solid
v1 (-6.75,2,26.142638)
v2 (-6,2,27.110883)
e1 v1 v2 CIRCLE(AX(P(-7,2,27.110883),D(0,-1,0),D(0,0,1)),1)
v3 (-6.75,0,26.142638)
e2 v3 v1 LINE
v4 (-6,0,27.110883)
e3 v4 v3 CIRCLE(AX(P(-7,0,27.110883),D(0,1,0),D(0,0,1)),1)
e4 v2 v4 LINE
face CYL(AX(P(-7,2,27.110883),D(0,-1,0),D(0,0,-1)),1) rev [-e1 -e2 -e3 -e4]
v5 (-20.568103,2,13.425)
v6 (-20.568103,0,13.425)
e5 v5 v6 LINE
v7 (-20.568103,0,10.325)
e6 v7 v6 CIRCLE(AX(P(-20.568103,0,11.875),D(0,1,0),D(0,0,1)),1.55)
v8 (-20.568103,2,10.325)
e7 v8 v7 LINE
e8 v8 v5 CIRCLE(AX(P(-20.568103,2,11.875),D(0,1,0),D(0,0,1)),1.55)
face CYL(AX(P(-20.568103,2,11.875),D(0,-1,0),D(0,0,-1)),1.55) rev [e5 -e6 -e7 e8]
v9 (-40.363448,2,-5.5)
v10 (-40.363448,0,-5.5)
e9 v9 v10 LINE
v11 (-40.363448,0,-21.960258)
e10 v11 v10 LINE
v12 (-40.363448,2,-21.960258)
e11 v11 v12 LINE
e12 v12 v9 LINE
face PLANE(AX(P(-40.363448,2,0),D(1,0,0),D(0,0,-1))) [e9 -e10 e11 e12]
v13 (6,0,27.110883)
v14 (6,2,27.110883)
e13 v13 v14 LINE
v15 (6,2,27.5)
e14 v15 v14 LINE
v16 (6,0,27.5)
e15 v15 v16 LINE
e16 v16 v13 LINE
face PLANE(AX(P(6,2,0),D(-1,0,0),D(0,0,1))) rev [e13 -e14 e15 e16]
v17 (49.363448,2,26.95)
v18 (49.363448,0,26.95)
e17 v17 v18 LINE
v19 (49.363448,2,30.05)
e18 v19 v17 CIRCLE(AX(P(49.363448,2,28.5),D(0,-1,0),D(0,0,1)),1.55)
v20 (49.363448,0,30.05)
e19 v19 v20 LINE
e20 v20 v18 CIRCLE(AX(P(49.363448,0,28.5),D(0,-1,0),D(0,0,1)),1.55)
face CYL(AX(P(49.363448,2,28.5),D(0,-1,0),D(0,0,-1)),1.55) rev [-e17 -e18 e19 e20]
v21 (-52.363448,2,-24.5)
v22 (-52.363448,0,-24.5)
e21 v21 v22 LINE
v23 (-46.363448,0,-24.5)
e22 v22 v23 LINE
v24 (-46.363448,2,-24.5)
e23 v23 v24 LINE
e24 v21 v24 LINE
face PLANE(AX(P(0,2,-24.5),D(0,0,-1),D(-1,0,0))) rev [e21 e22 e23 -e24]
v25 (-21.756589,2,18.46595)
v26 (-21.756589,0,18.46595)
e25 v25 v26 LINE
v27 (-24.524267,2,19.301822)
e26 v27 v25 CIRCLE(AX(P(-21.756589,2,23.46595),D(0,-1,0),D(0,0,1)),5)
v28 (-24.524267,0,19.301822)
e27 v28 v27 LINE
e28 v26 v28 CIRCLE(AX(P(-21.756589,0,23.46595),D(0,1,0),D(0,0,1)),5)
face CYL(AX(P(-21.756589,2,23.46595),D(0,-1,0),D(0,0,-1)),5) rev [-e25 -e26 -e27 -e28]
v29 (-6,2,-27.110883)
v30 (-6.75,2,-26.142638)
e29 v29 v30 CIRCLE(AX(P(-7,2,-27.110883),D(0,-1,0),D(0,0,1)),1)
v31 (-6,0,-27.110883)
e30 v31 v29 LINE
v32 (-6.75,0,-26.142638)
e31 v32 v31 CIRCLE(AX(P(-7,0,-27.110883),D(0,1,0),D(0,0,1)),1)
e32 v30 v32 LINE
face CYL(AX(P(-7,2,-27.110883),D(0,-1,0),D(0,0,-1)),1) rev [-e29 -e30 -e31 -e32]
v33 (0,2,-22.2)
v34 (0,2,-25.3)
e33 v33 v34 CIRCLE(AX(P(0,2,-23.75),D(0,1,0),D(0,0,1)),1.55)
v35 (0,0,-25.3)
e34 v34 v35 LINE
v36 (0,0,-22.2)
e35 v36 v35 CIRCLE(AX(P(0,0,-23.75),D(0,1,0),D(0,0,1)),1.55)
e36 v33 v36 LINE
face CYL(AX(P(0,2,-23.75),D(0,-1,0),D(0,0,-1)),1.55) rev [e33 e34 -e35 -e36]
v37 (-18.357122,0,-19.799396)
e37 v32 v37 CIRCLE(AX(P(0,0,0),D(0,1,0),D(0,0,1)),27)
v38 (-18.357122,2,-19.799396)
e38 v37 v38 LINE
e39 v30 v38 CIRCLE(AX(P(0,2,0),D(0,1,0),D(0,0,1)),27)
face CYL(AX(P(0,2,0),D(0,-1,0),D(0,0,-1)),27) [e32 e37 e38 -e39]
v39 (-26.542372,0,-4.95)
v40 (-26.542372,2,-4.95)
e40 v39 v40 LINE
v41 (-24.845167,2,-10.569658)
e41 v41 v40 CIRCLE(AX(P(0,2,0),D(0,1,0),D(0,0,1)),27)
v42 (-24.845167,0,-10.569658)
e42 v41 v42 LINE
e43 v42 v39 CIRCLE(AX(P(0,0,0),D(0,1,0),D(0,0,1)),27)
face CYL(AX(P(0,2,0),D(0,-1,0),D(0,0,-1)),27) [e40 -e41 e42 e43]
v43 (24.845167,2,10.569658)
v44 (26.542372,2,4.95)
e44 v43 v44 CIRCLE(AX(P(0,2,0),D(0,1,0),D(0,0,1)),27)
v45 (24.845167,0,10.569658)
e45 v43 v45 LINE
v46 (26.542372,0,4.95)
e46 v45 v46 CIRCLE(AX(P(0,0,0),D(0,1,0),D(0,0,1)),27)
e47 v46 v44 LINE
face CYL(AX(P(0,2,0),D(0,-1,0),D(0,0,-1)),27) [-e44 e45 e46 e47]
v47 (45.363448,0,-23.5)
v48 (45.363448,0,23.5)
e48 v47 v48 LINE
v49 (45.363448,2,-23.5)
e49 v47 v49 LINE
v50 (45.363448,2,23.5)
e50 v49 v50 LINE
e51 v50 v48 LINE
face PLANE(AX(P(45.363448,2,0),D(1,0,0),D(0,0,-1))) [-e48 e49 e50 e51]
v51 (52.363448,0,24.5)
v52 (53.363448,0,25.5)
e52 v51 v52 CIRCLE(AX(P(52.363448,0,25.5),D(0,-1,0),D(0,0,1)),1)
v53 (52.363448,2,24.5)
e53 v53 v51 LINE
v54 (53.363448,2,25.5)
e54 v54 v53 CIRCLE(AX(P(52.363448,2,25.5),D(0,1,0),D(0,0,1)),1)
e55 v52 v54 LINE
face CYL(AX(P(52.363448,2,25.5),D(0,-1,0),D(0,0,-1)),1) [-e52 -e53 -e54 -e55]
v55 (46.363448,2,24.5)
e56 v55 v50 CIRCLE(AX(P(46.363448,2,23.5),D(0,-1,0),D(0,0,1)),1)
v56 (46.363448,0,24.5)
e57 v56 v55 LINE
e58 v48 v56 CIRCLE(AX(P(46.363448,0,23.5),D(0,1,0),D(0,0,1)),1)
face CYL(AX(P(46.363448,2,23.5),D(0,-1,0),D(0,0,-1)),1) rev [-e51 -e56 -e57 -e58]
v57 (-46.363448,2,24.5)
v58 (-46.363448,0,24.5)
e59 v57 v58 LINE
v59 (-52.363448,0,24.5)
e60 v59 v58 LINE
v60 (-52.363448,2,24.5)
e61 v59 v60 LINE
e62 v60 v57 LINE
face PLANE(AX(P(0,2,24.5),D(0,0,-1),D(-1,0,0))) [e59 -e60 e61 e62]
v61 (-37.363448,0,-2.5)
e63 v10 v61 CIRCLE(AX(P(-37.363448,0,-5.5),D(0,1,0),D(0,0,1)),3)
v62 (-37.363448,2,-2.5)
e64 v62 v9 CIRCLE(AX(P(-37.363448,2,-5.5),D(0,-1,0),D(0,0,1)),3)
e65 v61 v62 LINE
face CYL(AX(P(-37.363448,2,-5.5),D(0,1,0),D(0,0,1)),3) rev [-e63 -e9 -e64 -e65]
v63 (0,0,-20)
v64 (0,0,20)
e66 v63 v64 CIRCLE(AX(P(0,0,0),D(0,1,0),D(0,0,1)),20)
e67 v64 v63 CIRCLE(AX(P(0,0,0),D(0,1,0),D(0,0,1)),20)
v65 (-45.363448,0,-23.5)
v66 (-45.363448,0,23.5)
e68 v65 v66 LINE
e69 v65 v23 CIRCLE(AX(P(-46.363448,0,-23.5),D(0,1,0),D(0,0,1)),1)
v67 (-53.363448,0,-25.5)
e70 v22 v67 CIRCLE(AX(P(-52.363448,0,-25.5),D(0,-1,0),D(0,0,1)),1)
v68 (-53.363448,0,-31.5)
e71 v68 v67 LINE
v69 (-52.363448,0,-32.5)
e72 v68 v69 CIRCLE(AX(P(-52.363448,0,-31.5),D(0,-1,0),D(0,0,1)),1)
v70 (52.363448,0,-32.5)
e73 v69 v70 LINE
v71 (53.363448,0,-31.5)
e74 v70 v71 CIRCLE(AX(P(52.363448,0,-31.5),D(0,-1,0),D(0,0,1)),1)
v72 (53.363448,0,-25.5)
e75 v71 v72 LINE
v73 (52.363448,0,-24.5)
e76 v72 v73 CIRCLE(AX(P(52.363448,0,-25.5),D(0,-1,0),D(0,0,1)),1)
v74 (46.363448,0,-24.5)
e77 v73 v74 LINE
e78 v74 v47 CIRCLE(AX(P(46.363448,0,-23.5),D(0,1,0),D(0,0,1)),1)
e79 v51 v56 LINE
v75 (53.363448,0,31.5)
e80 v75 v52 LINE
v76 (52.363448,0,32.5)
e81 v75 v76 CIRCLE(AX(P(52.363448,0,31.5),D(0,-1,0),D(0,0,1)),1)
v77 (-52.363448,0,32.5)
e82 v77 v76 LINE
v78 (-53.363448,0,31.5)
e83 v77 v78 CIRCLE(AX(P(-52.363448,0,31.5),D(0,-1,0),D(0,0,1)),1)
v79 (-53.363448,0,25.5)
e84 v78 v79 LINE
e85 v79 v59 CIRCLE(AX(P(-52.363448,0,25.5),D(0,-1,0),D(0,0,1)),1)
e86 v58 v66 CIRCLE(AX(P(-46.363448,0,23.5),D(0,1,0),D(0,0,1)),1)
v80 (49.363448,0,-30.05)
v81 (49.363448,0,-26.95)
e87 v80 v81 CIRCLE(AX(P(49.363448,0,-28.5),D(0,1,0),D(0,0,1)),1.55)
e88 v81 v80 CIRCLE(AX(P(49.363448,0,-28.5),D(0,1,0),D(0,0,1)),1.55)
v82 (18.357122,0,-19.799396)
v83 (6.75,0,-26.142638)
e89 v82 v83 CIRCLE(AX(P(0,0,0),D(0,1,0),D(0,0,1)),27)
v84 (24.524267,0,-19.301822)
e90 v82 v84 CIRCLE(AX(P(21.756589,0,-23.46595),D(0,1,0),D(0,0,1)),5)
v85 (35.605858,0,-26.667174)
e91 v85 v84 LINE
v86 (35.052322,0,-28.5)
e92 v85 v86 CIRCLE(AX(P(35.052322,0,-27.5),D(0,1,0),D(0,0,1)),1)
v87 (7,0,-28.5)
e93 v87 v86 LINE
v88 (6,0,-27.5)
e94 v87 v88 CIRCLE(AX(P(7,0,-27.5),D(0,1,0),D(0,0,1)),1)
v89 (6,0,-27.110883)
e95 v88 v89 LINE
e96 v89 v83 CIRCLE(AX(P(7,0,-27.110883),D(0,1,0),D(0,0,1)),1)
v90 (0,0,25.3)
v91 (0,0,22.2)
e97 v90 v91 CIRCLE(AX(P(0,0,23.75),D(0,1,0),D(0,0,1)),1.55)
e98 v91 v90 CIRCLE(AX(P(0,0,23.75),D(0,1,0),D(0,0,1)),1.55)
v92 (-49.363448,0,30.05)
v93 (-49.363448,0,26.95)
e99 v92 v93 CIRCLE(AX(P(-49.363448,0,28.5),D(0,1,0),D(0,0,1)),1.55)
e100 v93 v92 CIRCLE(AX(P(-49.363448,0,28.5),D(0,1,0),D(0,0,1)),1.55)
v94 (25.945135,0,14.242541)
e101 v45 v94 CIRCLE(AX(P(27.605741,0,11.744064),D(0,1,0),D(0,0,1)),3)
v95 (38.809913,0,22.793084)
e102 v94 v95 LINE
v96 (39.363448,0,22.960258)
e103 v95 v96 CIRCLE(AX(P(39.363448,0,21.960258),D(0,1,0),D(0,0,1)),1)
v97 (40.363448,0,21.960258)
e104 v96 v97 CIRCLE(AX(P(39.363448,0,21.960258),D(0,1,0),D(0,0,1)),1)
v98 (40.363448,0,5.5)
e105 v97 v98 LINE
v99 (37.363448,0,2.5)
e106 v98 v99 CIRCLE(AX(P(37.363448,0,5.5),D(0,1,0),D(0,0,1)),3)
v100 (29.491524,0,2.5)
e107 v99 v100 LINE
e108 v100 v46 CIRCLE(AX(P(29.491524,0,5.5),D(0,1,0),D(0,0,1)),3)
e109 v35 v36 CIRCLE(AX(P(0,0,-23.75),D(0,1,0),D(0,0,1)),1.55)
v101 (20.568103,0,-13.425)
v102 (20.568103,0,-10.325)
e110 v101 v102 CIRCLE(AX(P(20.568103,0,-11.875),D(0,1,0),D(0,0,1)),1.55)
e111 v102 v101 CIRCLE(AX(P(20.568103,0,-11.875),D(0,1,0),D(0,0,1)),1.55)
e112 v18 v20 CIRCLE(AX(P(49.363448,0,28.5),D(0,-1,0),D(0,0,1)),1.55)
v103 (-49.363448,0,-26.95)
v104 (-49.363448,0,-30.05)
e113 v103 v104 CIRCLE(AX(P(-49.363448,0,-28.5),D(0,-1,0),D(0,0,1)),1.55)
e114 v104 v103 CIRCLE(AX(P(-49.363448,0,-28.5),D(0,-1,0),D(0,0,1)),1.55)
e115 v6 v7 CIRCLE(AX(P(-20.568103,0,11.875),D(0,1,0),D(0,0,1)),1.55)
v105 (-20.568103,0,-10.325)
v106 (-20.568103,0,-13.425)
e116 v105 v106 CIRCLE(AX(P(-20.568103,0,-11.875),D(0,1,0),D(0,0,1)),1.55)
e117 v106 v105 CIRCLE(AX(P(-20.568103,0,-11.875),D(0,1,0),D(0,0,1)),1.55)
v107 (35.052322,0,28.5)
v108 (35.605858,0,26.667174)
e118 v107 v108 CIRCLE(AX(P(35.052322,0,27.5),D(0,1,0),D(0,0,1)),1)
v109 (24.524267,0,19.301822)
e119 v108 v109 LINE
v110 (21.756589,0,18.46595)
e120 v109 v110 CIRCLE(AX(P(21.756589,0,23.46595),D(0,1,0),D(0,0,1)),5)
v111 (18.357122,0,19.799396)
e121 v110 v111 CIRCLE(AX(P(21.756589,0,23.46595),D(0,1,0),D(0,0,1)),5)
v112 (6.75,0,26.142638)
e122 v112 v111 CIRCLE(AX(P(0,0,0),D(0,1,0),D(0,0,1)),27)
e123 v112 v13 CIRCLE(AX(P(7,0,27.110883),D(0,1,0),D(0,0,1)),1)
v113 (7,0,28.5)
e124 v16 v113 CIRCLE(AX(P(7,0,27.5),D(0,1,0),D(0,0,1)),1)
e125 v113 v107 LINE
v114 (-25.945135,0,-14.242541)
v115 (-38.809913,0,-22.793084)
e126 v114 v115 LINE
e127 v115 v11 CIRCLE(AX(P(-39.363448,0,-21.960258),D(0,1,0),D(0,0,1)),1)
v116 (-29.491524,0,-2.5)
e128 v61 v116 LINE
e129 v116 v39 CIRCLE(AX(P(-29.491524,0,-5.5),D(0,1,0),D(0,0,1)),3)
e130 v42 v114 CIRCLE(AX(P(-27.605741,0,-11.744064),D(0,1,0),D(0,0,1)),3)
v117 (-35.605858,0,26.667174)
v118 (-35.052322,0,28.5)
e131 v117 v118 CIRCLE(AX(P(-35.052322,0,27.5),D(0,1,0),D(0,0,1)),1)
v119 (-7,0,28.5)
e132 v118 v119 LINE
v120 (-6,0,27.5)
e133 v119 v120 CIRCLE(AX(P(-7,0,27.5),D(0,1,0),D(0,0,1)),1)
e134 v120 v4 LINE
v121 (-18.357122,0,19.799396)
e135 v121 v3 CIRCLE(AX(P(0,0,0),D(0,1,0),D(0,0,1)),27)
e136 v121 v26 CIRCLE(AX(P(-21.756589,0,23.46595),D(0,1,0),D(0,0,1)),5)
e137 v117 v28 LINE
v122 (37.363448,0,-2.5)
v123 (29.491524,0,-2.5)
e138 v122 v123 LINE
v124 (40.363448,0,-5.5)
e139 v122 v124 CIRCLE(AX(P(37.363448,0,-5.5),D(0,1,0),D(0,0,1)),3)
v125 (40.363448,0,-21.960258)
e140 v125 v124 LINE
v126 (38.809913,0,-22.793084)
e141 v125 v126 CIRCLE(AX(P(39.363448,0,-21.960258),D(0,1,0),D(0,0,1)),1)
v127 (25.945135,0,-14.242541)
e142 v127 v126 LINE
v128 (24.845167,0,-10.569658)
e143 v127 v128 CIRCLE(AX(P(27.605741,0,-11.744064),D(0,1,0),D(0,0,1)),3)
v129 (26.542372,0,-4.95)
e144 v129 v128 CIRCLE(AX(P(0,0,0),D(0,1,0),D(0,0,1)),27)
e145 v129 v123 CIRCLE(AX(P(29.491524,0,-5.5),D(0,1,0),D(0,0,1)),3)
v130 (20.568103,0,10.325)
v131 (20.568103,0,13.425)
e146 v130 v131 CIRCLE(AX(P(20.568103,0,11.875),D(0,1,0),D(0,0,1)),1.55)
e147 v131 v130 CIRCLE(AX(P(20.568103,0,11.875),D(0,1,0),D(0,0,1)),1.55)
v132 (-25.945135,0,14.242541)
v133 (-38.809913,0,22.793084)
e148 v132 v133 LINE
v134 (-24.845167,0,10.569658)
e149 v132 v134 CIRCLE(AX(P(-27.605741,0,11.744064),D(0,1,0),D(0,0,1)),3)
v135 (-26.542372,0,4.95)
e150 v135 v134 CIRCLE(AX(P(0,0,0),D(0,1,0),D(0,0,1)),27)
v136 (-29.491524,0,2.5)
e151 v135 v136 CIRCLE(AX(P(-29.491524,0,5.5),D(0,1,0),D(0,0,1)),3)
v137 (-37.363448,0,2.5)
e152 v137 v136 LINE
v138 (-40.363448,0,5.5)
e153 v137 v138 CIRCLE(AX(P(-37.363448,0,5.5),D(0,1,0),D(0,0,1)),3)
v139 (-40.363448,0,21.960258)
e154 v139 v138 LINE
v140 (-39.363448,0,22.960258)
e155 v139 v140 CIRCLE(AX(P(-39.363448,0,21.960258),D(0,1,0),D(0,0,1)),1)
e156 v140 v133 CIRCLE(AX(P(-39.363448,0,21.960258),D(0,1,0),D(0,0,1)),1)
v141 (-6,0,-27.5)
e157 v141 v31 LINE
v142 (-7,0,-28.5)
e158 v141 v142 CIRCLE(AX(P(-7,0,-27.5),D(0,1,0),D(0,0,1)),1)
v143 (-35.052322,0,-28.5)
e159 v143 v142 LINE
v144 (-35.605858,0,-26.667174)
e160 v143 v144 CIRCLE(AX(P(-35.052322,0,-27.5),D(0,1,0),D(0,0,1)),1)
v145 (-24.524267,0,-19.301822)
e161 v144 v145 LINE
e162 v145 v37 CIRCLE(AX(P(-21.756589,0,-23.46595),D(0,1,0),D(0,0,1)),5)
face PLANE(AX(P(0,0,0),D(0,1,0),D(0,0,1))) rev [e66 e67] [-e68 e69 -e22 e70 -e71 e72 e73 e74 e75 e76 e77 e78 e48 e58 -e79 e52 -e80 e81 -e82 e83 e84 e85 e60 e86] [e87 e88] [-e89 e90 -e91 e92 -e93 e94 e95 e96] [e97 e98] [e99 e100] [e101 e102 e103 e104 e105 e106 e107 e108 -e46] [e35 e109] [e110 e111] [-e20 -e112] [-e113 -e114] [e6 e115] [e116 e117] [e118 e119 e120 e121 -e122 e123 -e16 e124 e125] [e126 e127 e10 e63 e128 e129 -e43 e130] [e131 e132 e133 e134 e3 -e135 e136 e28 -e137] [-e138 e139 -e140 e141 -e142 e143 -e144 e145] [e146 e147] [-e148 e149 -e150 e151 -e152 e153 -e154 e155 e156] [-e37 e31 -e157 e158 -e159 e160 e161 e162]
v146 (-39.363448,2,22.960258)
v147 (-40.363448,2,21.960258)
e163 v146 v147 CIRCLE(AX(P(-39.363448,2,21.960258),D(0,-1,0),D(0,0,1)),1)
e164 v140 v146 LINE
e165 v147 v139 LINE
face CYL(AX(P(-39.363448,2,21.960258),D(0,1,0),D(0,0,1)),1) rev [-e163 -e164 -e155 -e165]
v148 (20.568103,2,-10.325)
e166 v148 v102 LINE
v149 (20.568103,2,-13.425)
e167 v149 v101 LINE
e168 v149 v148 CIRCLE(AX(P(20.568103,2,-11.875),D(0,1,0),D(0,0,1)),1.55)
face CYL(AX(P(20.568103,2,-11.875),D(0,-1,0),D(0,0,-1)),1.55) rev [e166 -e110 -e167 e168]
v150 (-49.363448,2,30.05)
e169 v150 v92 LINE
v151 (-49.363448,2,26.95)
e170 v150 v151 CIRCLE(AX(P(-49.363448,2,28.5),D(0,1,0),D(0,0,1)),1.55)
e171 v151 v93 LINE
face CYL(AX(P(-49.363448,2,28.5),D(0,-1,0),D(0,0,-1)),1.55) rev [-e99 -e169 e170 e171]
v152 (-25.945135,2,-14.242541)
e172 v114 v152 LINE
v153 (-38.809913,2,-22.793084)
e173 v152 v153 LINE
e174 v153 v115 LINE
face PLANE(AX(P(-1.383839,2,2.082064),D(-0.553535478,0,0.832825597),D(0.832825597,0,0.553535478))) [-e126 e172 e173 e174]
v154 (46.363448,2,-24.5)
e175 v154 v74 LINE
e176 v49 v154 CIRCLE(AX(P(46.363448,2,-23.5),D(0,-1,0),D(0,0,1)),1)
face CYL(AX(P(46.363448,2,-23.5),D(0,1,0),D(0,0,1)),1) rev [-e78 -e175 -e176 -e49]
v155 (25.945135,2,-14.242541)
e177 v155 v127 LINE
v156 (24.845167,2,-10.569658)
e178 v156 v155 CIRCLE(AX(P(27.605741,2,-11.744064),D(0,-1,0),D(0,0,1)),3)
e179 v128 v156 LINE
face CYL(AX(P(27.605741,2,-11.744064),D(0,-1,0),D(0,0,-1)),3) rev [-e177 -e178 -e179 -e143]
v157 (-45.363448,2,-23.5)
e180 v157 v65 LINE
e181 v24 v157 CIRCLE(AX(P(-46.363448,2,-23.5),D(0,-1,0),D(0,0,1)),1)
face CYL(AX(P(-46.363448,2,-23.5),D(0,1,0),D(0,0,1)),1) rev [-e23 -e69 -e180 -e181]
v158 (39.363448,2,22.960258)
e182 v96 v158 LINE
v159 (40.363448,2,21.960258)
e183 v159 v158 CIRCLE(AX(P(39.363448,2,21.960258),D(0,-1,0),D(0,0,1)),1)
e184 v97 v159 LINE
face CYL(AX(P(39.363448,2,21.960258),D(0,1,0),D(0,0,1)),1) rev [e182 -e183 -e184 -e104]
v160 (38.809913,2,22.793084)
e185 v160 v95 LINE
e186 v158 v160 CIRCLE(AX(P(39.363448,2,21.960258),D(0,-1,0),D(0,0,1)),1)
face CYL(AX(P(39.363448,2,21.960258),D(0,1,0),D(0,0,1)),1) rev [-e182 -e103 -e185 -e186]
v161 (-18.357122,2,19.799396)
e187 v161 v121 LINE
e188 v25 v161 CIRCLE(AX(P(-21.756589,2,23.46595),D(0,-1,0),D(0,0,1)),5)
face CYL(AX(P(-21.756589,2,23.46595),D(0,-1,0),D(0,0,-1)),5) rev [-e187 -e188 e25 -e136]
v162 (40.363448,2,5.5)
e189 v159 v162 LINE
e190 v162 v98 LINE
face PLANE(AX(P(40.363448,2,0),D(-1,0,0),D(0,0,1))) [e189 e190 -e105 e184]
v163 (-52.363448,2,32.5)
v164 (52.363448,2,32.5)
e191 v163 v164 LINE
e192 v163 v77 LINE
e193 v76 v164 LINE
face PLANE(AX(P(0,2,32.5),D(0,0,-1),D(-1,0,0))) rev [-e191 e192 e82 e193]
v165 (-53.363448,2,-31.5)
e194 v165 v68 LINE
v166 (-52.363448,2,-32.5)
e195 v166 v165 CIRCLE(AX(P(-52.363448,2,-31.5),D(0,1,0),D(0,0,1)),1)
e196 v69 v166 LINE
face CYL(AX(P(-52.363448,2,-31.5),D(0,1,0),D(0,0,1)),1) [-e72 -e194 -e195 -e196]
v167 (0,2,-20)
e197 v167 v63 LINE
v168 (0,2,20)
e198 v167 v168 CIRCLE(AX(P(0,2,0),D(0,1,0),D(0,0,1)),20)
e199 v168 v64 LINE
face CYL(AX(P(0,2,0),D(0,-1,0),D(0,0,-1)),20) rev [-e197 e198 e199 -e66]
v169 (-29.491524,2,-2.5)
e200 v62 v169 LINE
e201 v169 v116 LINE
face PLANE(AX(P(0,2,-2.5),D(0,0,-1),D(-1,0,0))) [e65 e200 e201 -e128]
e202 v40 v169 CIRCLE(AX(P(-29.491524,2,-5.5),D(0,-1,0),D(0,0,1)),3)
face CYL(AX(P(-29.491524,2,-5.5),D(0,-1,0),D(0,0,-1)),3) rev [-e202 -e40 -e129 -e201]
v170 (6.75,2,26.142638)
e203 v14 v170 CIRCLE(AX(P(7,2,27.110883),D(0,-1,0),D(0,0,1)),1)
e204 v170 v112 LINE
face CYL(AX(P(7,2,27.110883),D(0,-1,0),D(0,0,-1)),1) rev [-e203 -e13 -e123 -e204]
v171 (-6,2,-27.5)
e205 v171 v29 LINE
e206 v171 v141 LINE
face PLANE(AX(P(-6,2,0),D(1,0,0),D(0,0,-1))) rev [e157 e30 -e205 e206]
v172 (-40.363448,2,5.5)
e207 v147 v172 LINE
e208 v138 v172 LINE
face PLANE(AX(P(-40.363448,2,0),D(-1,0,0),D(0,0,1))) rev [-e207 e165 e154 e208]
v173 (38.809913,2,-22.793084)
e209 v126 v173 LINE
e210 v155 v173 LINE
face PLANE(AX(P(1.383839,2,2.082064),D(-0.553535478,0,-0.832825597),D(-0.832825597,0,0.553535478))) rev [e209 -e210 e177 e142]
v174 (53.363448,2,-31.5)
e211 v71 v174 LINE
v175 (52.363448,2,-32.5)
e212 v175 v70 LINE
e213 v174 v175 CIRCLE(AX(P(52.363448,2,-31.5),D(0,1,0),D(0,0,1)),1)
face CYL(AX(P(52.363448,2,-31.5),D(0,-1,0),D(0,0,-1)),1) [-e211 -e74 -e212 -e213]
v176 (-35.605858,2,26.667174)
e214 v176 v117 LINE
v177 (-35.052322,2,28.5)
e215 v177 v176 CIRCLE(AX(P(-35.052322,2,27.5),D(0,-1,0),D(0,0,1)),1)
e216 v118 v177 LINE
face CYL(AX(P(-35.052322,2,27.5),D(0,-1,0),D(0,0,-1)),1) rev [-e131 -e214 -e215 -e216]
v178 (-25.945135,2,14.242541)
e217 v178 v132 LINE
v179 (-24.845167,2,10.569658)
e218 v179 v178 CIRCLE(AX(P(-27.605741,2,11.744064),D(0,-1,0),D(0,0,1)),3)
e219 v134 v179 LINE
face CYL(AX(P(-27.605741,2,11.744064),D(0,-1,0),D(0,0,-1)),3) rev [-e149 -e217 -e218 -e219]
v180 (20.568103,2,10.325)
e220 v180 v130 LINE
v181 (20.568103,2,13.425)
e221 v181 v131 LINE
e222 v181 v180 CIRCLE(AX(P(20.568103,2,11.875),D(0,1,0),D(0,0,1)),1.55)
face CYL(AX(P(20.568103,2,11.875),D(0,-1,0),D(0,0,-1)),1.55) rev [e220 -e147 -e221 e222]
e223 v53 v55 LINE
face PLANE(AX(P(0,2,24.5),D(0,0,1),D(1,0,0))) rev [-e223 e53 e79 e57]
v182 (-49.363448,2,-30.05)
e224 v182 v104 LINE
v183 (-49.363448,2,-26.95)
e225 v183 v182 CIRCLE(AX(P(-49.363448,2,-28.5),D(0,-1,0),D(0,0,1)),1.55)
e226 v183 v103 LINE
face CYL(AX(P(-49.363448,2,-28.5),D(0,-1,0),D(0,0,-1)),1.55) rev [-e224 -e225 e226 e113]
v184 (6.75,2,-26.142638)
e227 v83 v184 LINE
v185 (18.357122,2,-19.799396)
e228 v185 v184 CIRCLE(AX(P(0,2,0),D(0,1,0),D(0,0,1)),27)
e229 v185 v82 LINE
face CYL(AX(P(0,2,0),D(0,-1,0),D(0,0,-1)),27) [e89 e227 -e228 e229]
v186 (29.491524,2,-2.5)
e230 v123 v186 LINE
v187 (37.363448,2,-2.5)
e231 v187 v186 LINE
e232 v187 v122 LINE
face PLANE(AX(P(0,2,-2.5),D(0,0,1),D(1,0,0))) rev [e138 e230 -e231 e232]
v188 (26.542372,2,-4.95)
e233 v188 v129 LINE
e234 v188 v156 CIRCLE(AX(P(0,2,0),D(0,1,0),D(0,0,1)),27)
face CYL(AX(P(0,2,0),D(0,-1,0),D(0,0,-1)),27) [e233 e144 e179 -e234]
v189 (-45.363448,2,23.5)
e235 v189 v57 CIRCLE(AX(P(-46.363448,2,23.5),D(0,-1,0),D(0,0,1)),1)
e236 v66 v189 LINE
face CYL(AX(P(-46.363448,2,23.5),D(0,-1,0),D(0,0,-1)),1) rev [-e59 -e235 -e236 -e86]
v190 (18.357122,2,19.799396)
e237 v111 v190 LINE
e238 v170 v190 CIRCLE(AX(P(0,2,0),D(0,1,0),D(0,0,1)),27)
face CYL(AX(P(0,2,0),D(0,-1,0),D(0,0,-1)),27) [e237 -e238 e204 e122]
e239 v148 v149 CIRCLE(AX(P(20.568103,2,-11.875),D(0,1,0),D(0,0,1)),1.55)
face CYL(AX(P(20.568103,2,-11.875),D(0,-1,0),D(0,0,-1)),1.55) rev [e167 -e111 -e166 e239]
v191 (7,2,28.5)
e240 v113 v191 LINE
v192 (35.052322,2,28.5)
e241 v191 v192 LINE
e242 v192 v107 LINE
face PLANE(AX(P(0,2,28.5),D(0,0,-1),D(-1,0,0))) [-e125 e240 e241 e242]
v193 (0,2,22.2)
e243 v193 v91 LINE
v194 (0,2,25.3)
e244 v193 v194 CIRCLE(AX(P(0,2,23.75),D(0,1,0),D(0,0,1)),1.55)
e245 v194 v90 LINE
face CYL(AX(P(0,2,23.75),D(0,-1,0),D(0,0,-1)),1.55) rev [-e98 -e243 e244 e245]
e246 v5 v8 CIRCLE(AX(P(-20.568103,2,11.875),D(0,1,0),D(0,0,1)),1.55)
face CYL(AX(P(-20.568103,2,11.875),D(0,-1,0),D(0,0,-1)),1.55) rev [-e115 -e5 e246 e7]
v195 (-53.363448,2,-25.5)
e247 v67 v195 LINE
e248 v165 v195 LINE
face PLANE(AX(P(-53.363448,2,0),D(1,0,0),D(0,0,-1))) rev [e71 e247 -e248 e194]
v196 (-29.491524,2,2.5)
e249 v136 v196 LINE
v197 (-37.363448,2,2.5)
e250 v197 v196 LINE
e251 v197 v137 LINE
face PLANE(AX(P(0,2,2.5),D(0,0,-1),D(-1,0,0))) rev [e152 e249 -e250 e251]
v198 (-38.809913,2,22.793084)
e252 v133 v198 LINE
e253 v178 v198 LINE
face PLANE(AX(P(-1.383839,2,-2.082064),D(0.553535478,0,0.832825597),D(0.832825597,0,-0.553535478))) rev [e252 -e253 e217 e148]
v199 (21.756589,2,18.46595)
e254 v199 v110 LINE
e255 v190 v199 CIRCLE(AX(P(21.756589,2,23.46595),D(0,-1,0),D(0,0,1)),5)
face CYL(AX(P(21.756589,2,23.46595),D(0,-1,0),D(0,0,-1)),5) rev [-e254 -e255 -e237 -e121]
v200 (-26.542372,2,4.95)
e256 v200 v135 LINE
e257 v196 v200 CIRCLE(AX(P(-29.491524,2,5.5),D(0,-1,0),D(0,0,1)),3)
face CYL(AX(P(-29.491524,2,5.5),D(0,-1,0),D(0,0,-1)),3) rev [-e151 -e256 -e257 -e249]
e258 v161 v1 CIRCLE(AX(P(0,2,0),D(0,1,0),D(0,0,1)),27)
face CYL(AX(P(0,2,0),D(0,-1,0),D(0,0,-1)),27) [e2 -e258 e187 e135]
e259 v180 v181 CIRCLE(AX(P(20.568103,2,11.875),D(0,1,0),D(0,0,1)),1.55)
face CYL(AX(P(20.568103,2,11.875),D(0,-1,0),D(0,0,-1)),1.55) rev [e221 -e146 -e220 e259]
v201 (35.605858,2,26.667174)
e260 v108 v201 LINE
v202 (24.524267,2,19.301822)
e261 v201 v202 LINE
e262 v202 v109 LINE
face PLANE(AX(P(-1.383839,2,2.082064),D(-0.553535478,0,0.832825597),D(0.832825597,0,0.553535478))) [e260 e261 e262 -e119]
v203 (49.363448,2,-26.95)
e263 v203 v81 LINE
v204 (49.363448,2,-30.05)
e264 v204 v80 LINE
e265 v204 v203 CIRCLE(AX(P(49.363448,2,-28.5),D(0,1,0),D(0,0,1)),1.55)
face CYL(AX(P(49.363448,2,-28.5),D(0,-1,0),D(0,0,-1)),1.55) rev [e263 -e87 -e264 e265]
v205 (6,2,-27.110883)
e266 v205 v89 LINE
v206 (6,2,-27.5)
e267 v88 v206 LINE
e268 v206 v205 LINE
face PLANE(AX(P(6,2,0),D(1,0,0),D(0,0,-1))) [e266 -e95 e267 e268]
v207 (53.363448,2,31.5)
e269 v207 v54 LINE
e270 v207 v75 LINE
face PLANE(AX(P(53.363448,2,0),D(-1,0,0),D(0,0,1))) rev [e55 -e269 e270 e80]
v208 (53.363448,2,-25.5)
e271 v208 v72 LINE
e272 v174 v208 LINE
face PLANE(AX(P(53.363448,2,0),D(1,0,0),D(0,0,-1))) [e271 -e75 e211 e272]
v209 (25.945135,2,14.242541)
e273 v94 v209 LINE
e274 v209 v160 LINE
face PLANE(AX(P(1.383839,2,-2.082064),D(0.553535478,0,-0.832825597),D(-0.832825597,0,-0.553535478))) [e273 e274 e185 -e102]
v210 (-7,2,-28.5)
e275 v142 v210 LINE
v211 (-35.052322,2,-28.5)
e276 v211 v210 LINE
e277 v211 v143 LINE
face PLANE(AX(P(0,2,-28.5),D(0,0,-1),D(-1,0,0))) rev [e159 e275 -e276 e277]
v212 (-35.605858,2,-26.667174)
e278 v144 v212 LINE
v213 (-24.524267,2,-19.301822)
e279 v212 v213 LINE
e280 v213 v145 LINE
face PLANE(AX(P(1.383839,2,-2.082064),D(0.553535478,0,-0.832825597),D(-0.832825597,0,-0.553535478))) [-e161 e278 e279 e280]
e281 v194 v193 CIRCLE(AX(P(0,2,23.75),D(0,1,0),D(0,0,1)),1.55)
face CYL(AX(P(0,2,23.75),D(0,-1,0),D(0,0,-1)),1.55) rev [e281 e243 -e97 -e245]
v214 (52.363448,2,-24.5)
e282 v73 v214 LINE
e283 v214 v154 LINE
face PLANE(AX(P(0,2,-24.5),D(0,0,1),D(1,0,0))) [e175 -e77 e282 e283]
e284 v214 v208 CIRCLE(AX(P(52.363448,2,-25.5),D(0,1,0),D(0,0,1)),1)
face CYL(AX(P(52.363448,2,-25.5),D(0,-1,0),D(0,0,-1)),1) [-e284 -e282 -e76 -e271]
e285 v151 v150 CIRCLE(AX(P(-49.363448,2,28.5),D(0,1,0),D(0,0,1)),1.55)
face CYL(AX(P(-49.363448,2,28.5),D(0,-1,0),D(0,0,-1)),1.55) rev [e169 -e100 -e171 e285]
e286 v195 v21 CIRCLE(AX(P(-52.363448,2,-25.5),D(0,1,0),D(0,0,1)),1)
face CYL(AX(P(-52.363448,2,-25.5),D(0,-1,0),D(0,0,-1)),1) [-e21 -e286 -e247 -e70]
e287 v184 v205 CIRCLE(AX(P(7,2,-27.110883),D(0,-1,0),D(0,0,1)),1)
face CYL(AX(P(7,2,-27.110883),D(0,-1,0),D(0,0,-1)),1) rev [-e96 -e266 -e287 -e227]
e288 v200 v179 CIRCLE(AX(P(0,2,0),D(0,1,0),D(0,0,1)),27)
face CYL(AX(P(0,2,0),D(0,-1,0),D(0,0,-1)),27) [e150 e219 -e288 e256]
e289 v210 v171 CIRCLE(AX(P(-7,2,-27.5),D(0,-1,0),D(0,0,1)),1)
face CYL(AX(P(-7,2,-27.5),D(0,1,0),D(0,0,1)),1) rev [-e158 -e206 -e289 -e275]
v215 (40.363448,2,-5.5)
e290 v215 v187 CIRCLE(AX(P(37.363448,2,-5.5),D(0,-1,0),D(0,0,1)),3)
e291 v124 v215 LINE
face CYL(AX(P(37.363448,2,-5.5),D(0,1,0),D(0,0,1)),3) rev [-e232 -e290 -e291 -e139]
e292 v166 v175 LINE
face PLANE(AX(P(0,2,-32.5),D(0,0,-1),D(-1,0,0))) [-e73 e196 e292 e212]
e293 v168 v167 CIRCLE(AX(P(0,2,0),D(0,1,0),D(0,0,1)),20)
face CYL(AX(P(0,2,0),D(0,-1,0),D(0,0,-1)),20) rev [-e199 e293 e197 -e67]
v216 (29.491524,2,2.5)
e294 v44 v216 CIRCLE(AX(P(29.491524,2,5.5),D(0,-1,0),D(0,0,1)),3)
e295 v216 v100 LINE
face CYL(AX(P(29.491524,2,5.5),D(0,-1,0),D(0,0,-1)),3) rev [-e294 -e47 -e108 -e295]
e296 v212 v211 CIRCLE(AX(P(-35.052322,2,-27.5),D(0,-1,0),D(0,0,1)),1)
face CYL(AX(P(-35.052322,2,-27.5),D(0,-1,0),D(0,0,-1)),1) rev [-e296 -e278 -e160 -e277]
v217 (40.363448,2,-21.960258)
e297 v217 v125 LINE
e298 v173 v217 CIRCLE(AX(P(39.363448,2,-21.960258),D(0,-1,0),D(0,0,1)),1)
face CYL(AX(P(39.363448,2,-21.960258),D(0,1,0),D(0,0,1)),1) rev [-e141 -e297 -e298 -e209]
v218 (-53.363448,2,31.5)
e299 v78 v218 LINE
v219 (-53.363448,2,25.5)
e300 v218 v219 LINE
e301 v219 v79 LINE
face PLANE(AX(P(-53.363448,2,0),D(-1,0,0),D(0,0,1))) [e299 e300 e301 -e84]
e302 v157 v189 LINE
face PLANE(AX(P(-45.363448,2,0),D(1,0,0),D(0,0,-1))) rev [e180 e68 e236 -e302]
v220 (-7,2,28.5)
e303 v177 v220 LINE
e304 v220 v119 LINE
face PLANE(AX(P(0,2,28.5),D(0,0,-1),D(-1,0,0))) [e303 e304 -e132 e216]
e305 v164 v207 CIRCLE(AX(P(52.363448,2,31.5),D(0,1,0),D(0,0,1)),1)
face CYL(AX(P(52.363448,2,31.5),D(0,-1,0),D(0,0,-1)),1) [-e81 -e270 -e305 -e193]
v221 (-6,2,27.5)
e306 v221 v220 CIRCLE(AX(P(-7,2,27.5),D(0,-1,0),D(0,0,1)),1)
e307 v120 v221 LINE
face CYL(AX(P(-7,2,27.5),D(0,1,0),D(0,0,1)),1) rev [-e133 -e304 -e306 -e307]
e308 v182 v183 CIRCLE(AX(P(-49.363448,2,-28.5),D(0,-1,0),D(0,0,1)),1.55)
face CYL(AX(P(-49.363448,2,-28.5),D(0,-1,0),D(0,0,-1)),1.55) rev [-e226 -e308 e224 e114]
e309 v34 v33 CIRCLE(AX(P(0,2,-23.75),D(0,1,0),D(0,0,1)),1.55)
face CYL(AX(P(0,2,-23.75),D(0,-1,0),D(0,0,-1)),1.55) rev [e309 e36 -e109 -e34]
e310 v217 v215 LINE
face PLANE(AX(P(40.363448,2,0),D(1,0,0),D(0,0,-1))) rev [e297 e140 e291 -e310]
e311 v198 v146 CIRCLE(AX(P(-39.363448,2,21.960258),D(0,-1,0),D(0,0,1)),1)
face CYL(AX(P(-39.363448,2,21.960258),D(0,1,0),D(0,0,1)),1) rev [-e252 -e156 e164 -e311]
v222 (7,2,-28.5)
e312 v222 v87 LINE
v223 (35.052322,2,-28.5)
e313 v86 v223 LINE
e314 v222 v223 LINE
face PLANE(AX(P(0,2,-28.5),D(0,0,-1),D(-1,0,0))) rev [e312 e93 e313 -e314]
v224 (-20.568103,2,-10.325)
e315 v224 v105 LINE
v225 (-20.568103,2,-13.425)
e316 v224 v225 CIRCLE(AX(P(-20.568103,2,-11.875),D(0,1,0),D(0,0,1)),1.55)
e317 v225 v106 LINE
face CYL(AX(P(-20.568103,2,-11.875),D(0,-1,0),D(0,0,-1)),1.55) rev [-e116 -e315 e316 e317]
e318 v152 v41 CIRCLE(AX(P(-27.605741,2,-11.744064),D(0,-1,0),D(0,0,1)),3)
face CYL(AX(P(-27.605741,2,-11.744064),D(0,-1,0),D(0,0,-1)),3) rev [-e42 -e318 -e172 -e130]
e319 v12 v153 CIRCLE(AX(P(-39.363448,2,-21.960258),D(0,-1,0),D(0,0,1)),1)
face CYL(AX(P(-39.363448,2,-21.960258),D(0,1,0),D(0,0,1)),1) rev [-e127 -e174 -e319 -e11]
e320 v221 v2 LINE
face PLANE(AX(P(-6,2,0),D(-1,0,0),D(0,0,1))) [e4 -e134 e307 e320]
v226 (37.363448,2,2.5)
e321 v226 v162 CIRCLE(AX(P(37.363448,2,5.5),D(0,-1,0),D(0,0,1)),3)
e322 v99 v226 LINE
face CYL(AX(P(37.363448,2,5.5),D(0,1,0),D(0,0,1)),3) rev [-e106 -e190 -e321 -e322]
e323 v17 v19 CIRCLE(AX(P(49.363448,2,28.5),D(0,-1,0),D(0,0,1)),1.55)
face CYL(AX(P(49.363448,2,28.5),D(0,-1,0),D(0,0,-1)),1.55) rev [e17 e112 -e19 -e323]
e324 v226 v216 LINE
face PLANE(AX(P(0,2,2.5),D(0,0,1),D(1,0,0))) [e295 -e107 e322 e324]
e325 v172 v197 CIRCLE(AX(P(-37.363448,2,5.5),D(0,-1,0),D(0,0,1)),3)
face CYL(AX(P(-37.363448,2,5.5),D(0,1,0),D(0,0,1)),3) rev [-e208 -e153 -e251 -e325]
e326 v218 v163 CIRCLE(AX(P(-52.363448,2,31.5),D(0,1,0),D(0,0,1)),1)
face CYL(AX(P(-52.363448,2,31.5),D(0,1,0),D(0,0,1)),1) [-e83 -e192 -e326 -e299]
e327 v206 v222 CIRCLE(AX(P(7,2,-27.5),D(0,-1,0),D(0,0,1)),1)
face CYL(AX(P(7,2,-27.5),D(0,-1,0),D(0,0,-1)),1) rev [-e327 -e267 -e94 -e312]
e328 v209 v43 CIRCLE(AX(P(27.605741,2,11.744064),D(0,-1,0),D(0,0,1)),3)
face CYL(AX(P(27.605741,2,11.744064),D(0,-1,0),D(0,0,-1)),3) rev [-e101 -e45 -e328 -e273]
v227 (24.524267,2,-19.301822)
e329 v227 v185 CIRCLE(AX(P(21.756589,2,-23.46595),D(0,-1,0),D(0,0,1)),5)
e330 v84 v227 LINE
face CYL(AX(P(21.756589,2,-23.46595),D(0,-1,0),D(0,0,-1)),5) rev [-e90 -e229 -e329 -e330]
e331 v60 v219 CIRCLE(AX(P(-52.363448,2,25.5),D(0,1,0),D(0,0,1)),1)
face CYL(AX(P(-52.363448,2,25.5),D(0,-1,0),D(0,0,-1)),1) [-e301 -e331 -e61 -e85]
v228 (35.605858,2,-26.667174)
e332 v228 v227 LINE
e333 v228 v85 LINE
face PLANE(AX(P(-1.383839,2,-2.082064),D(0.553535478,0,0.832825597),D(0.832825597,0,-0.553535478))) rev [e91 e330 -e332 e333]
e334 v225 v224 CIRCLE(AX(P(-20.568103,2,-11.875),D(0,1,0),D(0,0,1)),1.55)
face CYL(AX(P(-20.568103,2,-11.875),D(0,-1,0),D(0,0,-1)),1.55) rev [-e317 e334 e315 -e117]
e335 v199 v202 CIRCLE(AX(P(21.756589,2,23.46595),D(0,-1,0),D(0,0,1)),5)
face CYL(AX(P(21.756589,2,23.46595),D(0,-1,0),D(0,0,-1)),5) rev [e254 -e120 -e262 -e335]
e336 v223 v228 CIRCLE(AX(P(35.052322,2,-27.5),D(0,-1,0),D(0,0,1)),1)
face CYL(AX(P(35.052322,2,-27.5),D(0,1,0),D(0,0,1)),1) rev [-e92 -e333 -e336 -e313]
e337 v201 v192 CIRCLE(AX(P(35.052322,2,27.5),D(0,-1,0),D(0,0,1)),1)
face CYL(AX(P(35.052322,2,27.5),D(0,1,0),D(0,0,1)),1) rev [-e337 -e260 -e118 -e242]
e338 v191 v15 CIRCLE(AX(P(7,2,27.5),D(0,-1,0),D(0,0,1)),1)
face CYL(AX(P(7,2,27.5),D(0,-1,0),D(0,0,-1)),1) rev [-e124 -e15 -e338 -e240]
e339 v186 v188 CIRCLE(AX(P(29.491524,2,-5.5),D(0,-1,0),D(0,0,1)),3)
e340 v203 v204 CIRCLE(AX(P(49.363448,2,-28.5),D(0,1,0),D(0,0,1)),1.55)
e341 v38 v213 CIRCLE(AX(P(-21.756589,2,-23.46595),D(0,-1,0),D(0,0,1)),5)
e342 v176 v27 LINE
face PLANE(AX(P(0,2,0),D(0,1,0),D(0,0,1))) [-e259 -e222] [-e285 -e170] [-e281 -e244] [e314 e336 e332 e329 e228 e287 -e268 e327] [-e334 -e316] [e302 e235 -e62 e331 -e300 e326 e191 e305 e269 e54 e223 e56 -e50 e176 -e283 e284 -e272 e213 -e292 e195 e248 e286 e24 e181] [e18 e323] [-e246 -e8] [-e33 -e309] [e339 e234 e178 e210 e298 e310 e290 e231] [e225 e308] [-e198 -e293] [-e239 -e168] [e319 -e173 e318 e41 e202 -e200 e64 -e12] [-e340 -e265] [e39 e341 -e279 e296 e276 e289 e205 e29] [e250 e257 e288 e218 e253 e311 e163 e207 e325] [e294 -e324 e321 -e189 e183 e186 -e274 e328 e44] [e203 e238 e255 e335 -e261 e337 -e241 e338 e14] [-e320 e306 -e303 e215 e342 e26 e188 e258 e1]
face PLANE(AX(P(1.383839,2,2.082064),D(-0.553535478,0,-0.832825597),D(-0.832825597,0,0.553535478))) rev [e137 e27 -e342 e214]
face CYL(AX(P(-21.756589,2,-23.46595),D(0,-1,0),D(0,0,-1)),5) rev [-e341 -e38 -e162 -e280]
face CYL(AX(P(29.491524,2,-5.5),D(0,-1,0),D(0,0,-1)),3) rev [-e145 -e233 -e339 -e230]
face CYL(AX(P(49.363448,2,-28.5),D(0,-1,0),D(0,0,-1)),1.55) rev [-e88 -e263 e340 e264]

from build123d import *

# Parameters (mm, degrees)
SKETCH_1_R      = 1.55
SKETCH_1_R_2    = 20
EXTRUDE_1_DEPTH = 2
FILLET_1_R      = 1
FILLET_2_R      = 3
FILLET_3_R      = 5


with BuildPart() as part:
    # 草图1 → 凸台-拉伸1 (new body)
    with BuildSketch(Plane(origin=(0, 0, 0), x_dir=(1, 0, 0), z_dir=(0, 1, 0))):
        Polygon((-53.363448016, 32.5), (53.363448016, 32.5), (53.363448016, 24.5), (45.363448016, 24.5), (45.363448016, -24.5), (53.363448016, -24.5), (53.363448016, -32.5), (-53.363448016, -32.5), (-53.363448016, -24.5), (-45.363448016, -24.5), (-45.363448016, 24.5), (-53.363448016, 24.5), align=None)
        with Locations(Location((49.363448016, 28.5, 0), (0, 0, 270))):
            Circle(SKETCH_1_R, mode=Mode.SUBTRACT)
        with Locations(Location((49.363448016, -28.5, 0), (0, 0, 270))):
            Circle(SKETCH_1_R, mode=Mode.SUBTRACT)
        with Locations(Location((-49.363448016, 28.5, 0), (0, 0, 270))):
            Circle(SKETCH_1_R, mode=Mode.SUBTRACT)
        with Locations(Location((-49.363448016, -28.5, 0), (0, 0, 270))):
            Circle(SKETCH_1_R, mode=Mode.SUBTRACT)
        with Locations(Location((20.56810334, 11.875, 0), (0, 0, 270))):
            Circle(SKETCH_1_R, mode=Mode.SUBTRACT)
        with Locations(Location((0, 0, 0), (0, 0, 270))):
            Circle(SKETCH_1_R_2, mode=Mode.SUBTRACT)
        with Locations(Location((20.56810334, -11.875, 0), (0, 0, 270))):
            Circle(SKETCH_1_R, mode=Mode.SUBTRACT)
        with Locations(Location((0, -23.75, 0), (0, 0, 270))):
            Circle(SKETCH_1_R, mode=Mode.SUBTRACT)
        with Locations(Location((-20.56810334, -11.875, 0), (0, 0, 270))):
            Circle(SKETCH_1_R, mode=Mode.SUBTRACT)
        with Locations(Location((-20.56810334, 11.875, 0), (0, 0, 270))):
            Circle(SKETCH_1_R, mode=Mode.SUBTRACT)
        with Locations(Location((0, 23.75, 0), (0, 0, 270))):
            Circle(SKETCH_1_R, mode=Mode.SUBTRACT)
        with BuildLine():
            Line((-38.363448016, 28.5), (-6, 28.5))
            Line((-6, 28.5), (-6, 26.324893162))
            ThreePointArc((-6, 26.324893162), (-14.291214103, 22.907666827), (-21.005853084, 16.963317371))
            Line((-21.005853084, 16.963317371), (-38.363448016, 28.5))
        make_face(mode=Mode.SUBTRACT)
        with BuildLine():
            Line((-23.773530472, 12.799189385), (-40.363448016, 23.825637134))
            Line((-40.363448016, 23.825637134), (-40.363448016, 2.5))
            Line((-40.363448016, 2.5), (-26.884010118, 2.5))
            ThreePointArc((-26.884010118, 2.5), (-25.846952047, 7.806091843), (-23.773530472, 12.799189385))
        make_face(mode=Mode.SUBTRACT)
        with BuildLine():
            Line((-38.363448016, -28.5), (-6, -28.5))
            Line((-6, -28.5), (-6, -26.324893162))
            ThreePointArc((-6, -26.324893162), (-14.291214103, -22.907666827), (-21.005853084, -16.963317371))
            Line((-21.005853084, -16.963317371), (-38.363448016, -28.5))
        make_face(mode=Mode.SUBTRACT)
        with BuildLine():
            Line((-23.773530472, -12.799189385), (-40.363448016, -23.825637134))
            Line((-40.363448016, -23.825637134), (-40.363448016, -2.5))
            Line((-40.363448016, -2.5), (-26.884010118, -2.5))
            ThreePointArc((-26.884010118, -2.5), (-25.846952047, -7.806091843), (-23.773530472, -12.799189385))
        make_face(mode=Mode.SUBTRACT)
        with BuildLine():
            Line((38.363448016, -28.5), (21.005853084, -16.963317371))
            ThreePointArc((21.005853084, -16.963317371), (14.291214103, -22.907666827), (6, -26.324893162))
            Line((6, -26.324893162), (6, -28.5))
            Line((6, -28.5), (38.363448016, -28.5))
        make_face(mode=Mode.SUBTRACT)
        with BuildLine():
            Line((23.773530472, -12.799189385), (40.363448016, -23.825637134))
            Line((40.363448016, -23.825637134), (40.363448016, -2.5))
            Line((40.363448016, -2.5), (26.884010118, -2.5))
            ThreePointArc((26.884010118, -2.5), (25.846952047, -7.806091843), (23.773530472, -12.799189385))
        make_face(mode=Mode.SUBTRACT)
        with BuildLine():
            Line((40.363448016, 2.5), (26.884010118, 2.5))
            ThreePointArc((26.884010118, 2.5), (25.846952047, 7.806091843), (23.773530472, 12.799189385))
            Line((23.773530472, 12.799189385), (40.363448016, 23.825637134))
            Line((40.363448016, 23.825637134), (40.363448016, 2.5))
        make_face(mode=Mode.SUBTRACT)
        with BuildLine():
            Line((38.363448016, 28.5), (21.005853084, 16.963317371))
            ThreePointArc((21.005853084, 16.963317371), (14.291214103, 22.907666827), (6, 26.324893162))
            Line((6, 26.324893162), (6, 28.5))
            Line((6, 28.5), (38.363448016, 28.5))
        make_face(mode=Mode.SUBTRACT)
    extrude(amount=EXTRUDE_1_DEPTH)

    # 圆角1
    fillet_1_edges = [part.edges().sort_by_distance(p)[0] for p in [
        (38.363448016, 1, -28.5),
        (6, 1, -28.5),
        (6, 1, -26.324893162),
        (40.363448016, 1, -23.825637134),
        (40.363448016, 1, 23.825637134),
        (6, 1, 28.5),
        (38.363448016, 1, 28.5),
        (6, 1, 26.324893162),
        (-38.363448016, 1, 28.5),
        (-6, 1, 28.5),
        (-6, 1, 26.324893162),
        (-40.363448016, 1, 23.825637134),
        (-6, 1, -28.5),
        (-38.363448016, 1, -28.5),
        (-6, 1, -26.324893162),
        (-40.363448016, 1, -23.825637134),
        (53.363448016, 1, -32.5),
        (53.363448016, 1, -24.5),
        (45.363448016, 1, -24.5),
        (45.363448016, 1, 24.5),
        (53.363448016, 1, 24.5),
        (53.363448016, 1, 32.5),
        (-53.363448016, 1, 32.5),
        (-53.363448016, 1, 24.5),
        (-45.363448016, 1, 24.5),
        (-45.363448016, 1, -24.5),
        (-53.363448016, 1, -24.5),
        (-53.363448016, 1, -32.5),
    ]]
    fillet(fillet_1_edges, radius=FILLET_1_R)

    # 圆角2
    fillet_2_edges = [part.edges().sort_by_distance(p)[0] for p in [
        (40.363448016, 1, -2.5),
        (23.773530472, 1, -12.799189385),
        (26.884010118, 1, -2.5),
        (40.363448016, 1, 2.5),
        (26.884010118, 1, 2.5),
        (23.773530472, 1, 12.799189385),
        (-40.363448016, 1, 2.5),
        (-23.773530472, 1, 12.799189385),
        (-26.884010118, 1, 2.5),
        (-40.363448016, 1, -2.5),
        (-26.884010118, 1, -2.5),
        (-23.773530472, 1, -12.799189385),
    ]]
    fillet(fillet_2_edges, radius=FILLET_2_R)

    # 圆角3
    fillet_3_edges = [part.edges().sort_by_distance(p)[0] for p in [
        (21.005853084, 1, -16.963317371),
        (21.005853084, 1, 16.963317371),
        (-21.005853084, 1, 16.963317371),
        (-21.005853084, 1, -16.963317371),
    ]]
    fillet(fillet_3_edges, radius=FILLET_3_R)


solid = part.part
